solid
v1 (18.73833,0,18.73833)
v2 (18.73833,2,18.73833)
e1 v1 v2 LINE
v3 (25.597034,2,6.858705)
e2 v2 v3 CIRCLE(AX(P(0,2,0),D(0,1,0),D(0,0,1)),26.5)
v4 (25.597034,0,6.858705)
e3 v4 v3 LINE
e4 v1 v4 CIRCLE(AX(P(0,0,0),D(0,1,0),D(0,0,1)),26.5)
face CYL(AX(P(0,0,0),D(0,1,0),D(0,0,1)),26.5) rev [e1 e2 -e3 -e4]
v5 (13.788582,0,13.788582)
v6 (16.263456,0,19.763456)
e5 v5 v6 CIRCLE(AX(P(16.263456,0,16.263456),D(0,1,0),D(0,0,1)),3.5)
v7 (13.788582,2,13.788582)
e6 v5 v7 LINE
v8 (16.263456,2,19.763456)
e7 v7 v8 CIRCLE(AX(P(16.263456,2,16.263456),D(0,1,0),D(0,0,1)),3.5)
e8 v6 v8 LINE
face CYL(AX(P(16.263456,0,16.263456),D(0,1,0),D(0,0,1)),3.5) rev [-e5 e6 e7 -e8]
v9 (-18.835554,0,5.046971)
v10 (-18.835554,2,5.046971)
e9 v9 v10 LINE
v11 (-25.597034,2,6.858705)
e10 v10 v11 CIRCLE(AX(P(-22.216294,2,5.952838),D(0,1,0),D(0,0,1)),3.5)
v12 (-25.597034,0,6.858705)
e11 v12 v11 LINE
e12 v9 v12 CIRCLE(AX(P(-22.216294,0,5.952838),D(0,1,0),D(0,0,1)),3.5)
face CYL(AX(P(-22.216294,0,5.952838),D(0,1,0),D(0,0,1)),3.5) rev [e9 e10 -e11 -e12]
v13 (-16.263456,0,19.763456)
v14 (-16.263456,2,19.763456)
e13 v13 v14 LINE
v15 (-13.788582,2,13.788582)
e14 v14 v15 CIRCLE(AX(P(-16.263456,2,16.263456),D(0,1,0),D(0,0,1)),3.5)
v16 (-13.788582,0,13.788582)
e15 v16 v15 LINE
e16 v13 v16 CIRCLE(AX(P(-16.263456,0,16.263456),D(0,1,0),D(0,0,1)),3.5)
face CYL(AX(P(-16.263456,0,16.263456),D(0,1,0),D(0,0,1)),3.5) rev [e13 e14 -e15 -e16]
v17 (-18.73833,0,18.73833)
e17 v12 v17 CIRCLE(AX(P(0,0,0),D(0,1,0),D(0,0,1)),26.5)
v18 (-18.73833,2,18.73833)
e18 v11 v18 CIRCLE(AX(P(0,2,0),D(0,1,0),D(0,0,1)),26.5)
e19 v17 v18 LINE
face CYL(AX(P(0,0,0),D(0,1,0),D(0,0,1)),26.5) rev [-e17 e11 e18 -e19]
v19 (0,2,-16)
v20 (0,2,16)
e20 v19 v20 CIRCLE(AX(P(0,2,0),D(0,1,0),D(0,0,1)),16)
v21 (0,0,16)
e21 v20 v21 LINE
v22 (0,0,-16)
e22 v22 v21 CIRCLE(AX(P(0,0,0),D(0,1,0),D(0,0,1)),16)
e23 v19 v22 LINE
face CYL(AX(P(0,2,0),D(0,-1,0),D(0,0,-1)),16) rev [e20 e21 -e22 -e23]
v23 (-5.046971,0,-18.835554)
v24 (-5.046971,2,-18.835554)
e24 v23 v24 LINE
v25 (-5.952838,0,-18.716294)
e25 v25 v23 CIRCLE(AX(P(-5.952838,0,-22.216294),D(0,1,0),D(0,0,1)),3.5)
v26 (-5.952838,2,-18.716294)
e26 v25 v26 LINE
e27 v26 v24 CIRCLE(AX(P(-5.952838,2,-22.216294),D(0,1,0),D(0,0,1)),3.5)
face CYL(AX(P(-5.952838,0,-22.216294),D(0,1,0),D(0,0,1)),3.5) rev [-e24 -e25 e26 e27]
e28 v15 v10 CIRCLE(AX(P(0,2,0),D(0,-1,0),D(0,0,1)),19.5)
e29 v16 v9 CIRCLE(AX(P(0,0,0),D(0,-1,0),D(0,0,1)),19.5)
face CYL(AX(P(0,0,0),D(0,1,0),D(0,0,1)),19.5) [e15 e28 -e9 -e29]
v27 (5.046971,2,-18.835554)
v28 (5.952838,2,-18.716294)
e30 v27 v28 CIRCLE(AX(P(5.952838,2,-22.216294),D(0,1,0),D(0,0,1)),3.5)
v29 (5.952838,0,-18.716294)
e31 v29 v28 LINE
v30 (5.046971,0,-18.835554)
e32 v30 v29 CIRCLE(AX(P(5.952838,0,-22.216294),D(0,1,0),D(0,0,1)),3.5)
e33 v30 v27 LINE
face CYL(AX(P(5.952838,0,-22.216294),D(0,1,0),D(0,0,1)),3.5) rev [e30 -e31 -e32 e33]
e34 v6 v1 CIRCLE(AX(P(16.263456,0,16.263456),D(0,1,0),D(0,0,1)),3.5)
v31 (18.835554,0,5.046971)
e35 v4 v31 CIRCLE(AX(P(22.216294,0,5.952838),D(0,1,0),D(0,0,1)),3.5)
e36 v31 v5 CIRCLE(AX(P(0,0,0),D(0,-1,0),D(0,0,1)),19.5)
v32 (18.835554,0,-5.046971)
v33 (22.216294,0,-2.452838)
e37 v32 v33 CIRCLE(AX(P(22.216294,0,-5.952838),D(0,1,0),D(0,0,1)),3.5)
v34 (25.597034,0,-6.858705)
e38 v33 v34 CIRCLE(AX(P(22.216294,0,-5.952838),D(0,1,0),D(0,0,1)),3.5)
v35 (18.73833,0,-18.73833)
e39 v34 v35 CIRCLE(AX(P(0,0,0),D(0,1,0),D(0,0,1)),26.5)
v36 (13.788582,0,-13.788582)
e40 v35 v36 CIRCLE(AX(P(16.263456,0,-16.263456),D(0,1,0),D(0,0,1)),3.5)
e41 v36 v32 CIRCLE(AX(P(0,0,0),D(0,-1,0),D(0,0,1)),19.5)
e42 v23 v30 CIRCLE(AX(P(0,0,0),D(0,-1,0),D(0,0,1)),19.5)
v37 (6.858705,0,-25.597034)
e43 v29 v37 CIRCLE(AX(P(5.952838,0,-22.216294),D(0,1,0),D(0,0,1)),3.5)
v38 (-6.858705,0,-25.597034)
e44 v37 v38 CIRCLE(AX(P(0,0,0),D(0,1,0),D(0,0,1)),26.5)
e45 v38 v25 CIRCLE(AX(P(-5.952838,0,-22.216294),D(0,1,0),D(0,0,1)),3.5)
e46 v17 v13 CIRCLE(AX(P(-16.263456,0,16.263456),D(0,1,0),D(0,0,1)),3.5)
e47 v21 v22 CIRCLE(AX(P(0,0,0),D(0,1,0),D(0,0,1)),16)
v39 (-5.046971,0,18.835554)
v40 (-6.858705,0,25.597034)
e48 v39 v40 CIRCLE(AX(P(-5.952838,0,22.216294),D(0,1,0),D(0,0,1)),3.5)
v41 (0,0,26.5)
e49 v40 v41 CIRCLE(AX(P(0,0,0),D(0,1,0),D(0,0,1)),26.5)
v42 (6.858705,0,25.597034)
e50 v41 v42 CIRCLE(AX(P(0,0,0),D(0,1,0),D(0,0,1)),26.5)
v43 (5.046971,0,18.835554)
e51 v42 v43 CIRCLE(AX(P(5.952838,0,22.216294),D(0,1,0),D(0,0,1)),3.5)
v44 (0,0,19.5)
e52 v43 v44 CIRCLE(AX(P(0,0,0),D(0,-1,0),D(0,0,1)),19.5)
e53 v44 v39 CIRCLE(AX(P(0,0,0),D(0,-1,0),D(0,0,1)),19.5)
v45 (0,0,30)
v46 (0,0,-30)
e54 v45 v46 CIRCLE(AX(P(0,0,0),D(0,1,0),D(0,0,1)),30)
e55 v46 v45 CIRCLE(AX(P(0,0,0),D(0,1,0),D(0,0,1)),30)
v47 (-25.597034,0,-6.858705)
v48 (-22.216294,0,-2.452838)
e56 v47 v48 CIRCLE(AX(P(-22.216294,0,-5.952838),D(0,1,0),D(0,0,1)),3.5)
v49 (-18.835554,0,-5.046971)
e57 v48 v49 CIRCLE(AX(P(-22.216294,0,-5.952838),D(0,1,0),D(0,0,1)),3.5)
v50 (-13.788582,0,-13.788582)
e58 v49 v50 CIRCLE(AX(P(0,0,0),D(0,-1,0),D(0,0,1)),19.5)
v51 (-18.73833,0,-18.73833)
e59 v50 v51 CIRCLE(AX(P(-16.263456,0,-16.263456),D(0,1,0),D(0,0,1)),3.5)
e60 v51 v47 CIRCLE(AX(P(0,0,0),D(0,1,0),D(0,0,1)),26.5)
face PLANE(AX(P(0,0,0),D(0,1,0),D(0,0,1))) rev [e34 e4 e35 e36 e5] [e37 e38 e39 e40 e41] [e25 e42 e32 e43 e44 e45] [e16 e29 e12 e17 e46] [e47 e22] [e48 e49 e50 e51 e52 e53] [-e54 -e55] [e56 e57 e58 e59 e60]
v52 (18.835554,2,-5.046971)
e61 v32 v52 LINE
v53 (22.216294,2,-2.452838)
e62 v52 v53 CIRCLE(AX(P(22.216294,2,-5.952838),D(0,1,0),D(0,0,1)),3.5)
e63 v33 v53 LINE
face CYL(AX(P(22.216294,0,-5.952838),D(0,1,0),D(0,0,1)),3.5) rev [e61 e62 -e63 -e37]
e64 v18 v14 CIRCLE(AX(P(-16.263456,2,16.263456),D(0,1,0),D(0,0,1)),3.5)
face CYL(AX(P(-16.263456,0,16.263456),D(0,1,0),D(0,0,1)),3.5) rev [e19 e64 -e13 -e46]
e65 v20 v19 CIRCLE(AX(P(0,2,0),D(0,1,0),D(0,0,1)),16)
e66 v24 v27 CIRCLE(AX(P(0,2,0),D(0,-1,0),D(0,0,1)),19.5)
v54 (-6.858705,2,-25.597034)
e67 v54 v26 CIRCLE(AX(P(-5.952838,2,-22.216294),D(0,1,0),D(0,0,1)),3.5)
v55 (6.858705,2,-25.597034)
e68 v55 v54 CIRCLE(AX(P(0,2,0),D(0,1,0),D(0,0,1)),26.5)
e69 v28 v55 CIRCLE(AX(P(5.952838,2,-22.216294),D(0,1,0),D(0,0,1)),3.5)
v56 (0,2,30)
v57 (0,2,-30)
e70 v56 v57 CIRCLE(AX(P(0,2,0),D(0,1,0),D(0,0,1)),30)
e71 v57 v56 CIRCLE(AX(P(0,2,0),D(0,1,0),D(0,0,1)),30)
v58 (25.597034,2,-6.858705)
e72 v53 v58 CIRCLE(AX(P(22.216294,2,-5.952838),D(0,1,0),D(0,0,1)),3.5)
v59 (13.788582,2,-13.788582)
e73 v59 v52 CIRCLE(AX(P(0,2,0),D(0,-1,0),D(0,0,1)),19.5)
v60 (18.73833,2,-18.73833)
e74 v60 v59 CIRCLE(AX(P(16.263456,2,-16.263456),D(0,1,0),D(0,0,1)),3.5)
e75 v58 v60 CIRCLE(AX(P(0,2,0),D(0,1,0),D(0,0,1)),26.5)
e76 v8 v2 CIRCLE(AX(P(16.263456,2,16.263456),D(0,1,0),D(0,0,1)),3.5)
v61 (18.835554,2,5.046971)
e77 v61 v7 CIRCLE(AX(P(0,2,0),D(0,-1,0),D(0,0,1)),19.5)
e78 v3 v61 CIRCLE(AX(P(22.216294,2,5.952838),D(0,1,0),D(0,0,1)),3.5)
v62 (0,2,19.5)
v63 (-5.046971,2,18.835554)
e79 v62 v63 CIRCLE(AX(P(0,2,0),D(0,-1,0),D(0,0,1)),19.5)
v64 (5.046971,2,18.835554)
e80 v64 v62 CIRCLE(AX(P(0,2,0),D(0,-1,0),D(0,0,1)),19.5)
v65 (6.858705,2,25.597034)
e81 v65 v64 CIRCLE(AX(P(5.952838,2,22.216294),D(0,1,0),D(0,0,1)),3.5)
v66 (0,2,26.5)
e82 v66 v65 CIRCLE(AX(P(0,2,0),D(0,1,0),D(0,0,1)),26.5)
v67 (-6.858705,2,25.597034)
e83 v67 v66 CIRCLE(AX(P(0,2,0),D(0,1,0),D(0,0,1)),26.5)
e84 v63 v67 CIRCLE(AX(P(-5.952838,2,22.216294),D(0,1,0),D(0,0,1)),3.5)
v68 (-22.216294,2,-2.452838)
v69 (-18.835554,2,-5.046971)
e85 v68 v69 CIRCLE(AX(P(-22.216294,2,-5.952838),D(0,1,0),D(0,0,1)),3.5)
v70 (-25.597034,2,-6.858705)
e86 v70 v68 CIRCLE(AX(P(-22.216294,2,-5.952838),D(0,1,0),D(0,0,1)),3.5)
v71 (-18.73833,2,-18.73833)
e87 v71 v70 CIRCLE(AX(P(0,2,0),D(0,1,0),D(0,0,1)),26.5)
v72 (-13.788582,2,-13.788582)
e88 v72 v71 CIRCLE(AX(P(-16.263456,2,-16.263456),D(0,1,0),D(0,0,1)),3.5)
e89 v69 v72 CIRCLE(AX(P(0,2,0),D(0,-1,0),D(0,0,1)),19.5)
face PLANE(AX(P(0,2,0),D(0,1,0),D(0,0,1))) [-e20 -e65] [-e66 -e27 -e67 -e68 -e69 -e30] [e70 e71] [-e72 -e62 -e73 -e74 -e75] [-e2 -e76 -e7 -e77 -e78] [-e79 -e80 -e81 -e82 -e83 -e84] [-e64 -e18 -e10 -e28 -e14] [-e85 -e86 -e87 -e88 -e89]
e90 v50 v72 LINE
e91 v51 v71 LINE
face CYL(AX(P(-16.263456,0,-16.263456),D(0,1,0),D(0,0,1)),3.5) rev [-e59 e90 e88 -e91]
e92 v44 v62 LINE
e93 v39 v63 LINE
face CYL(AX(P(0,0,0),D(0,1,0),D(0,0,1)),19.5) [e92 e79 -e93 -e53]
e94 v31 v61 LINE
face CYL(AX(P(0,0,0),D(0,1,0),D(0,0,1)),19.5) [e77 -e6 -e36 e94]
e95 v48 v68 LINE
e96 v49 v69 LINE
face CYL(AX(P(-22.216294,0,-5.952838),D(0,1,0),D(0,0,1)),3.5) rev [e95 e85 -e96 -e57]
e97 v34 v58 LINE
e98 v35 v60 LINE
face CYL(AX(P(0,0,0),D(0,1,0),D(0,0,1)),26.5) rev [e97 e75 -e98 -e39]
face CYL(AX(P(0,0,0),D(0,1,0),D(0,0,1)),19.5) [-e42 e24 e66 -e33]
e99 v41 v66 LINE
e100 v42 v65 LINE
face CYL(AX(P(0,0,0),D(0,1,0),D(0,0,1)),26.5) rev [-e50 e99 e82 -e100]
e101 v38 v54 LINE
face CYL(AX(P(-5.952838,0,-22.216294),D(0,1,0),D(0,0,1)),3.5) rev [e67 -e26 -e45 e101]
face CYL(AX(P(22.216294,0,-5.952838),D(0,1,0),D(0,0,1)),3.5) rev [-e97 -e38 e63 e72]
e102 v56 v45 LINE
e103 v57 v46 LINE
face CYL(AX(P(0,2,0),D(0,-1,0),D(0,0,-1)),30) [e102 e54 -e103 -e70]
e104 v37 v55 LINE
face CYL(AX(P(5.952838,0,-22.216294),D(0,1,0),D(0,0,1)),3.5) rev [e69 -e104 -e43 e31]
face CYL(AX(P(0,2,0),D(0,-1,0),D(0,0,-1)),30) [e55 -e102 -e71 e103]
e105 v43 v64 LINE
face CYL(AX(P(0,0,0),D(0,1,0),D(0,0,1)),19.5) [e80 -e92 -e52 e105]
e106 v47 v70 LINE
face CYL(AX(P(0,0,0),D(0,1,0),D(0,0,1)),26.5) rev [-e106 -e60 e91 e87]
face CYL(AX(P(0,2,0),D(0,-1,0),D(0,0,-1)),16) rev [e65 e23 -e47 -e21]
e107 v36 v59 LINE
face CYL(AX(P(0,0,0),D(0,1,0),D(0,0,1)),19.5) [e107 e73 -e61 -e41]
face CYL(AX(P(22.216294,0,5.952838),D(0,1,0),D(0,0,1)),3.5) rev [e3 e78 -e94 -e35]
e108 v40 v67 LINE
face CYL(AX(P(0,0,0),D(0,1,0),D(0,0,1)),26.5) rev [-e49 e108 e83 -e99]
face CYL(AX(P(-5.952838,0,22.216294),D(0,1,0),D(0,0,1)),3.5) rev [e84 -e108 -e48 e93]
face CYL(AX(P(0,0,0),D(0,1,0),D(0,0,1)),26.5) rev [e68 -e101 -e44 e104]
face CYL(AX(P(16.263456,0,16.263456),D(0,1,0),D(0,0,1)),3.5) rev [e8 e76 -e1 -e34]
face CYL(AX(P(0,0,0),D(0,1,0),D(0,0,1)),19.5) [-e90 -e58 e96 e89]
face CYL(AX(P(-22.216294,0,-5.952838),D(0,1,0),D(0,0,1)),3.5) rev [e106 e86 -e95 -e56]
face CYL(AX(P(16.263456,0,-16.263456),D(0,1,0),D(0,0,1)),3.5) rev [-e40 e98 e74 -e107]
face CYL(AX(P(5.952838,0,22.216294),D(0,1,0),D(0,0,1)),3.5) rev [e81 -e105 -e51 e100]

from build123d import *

# Parameters (mm, degrees)
SKETCH_1_R               = 30
SKETCH_1_R_2             = 16
EXTRUDE_1_DEPTH          = 2
CUT_EXTRUDE_1_DEPTH      = 43.473521163
CUT_EXTRUDE_1_DEPTH_BACK = 43.473521163


with BuildPart() as part:
    # 草图1 → 凸台-拉伸1 (new body)
    with BuildSketch(Plane(origin=(0, 0, 0), x_dir=(1, 0, 0), z_dir=(0, 1, 0))):
        with Locations(Location((0, 0, 0), (0, 0, 270))):
            Circle(SKETCH_1_R)
        with Locations(Location((0, 0, 0), (0, 0, 270))):
            Circle(SKETCH_1_R_2, mode=Mode.SUBTRACT)
    extrude(amount=EXTRUDE_1_DEPTH)

    # 草图2 → 切除-拉伸1 (cut, two sides: drawn at the far end of the back side and taken through both)
    with BuildSketch(Plane(origin=(0, 2, 0), x_dir=(1, 0, 0), z_dir=(0, 1, 0)).offset(-CUT_EXTRUDE_1_DEPTH_BACK)):
        with BuildLine():
            ThreePointArc((6.858704695, 25.597034397), (0, 26.5), (-6.858704695, 25.597034397))
            ThreePointArc((-6.858704695, 25.597034397), (-9.333578429, 21.310427347), (-5.046971379, 18.835553613))
            ThreePointArc((-5.046971379, 18.835553613), (0, 19.5), (5.046971379, 18.835553613))
            ThreePointArc((5.046971379, 18.835553613), (9.333578429, 21.310427347), (6.858704695, 25.597034397))
        make_face()
        with BuildLine():
            ThreePointArc((25.597034397, 6.858704695), (22.9496732, 13.25), (18.738329701, 18.738329701))
            ThreePointArc((18.738329701, 18.738329701), (13.788582233, 18.738329701), (13.788582233, 13.788582233))
            ThreePointArc((13.788582233, 13.788582233), (16.887495374, 9.75), (18.835553613, 5.046971379))
            ThreePointArc((18.835553613, 5.046971379), (23.122160663, 2.572097645), (25.597034397, 6.858704695))
        make_face()
        with BuildLine():
            ThreePointArc((18.738329701, -18.738329701), (22.9496732, -13.25), (25.597034397, -6.858704695))
            ThreePointArc((25.597034397, -6.858704695), (23.122160663, -2.572097645), (18.835553613, -5.046971379))
            ThreePointArc((18.835553613, -5.046971379), (16.887495374, -9.75), (13.788582233, -13.788582233))
            ThreePointArc((13.788582233, -13.788582233), (13.788582233, -18.738329701), (18.738329701, -18.738329701))
        make_face()
        with BuildLine():
            ThreePointArc((-6.858704695, -25.597034397), (0, -26.5), (6.858704695, -25.597034397))
            ThreePointArc((6.858704695, -25.597034397), (9.333578429, -21.310427347), (5.046971379, -18.835553613))
            ThreePointArc((5.046971379, -18.835553613), (0, -19.5), (-5.046971379, -18.835553613))
            ThreePointArc((-5.046971379, -18.835553613), (-9.333578429, -21.310427347), (-6.858704695, -25.597034397))
        make_face()
        with BuildLine():
            ThreePointArc((-25.597034397, -6.858704695), (-22.9496732, -13.25), (-18.738329701, -18.738329701))
            ThreePointArc((-18.738329701, -18.738329701), (-13.788582233, -18.738329701), (-13.788582233, -13.788582233))
            ThreePointArc((-13.788582233, -13.788582233), (-16.887495374, -9.75), (-18.835553613, -5.046971379))
            ThreePointArc((-18.835553613, -5.046971379), (-23.122160663, -2.572097645), (-25.597034397, -6.858704695))
        make_face()
        with BuildLine():
            ThreePointArc((-18.738329701, 18.738329701), (-22.9496732, 13.25), (-25.597034397, 6.858704695))
            ThreePointArc((-25.597034397, 6.858704695), (-23.122160663, 2.572097645), (-18.835553613, 5.046971379))
            ThreePointArc((-18.835553613, 5.046971379), (-16.887495374, 9.75), (-13.788582233, 13.788582233))
            ThreePointArc((-13.788582233, 13.788582233), (-13.788582233, 18.738329701), (-18.738329701, 18.738329701))
        make_face()
    extrude(amount=CUT_EXTRUDE_1_DEPTH + CUT_EXTRUDE_1_DEPTH_BACK, mode=Mode.SUBTRACT)


solid = part.part
